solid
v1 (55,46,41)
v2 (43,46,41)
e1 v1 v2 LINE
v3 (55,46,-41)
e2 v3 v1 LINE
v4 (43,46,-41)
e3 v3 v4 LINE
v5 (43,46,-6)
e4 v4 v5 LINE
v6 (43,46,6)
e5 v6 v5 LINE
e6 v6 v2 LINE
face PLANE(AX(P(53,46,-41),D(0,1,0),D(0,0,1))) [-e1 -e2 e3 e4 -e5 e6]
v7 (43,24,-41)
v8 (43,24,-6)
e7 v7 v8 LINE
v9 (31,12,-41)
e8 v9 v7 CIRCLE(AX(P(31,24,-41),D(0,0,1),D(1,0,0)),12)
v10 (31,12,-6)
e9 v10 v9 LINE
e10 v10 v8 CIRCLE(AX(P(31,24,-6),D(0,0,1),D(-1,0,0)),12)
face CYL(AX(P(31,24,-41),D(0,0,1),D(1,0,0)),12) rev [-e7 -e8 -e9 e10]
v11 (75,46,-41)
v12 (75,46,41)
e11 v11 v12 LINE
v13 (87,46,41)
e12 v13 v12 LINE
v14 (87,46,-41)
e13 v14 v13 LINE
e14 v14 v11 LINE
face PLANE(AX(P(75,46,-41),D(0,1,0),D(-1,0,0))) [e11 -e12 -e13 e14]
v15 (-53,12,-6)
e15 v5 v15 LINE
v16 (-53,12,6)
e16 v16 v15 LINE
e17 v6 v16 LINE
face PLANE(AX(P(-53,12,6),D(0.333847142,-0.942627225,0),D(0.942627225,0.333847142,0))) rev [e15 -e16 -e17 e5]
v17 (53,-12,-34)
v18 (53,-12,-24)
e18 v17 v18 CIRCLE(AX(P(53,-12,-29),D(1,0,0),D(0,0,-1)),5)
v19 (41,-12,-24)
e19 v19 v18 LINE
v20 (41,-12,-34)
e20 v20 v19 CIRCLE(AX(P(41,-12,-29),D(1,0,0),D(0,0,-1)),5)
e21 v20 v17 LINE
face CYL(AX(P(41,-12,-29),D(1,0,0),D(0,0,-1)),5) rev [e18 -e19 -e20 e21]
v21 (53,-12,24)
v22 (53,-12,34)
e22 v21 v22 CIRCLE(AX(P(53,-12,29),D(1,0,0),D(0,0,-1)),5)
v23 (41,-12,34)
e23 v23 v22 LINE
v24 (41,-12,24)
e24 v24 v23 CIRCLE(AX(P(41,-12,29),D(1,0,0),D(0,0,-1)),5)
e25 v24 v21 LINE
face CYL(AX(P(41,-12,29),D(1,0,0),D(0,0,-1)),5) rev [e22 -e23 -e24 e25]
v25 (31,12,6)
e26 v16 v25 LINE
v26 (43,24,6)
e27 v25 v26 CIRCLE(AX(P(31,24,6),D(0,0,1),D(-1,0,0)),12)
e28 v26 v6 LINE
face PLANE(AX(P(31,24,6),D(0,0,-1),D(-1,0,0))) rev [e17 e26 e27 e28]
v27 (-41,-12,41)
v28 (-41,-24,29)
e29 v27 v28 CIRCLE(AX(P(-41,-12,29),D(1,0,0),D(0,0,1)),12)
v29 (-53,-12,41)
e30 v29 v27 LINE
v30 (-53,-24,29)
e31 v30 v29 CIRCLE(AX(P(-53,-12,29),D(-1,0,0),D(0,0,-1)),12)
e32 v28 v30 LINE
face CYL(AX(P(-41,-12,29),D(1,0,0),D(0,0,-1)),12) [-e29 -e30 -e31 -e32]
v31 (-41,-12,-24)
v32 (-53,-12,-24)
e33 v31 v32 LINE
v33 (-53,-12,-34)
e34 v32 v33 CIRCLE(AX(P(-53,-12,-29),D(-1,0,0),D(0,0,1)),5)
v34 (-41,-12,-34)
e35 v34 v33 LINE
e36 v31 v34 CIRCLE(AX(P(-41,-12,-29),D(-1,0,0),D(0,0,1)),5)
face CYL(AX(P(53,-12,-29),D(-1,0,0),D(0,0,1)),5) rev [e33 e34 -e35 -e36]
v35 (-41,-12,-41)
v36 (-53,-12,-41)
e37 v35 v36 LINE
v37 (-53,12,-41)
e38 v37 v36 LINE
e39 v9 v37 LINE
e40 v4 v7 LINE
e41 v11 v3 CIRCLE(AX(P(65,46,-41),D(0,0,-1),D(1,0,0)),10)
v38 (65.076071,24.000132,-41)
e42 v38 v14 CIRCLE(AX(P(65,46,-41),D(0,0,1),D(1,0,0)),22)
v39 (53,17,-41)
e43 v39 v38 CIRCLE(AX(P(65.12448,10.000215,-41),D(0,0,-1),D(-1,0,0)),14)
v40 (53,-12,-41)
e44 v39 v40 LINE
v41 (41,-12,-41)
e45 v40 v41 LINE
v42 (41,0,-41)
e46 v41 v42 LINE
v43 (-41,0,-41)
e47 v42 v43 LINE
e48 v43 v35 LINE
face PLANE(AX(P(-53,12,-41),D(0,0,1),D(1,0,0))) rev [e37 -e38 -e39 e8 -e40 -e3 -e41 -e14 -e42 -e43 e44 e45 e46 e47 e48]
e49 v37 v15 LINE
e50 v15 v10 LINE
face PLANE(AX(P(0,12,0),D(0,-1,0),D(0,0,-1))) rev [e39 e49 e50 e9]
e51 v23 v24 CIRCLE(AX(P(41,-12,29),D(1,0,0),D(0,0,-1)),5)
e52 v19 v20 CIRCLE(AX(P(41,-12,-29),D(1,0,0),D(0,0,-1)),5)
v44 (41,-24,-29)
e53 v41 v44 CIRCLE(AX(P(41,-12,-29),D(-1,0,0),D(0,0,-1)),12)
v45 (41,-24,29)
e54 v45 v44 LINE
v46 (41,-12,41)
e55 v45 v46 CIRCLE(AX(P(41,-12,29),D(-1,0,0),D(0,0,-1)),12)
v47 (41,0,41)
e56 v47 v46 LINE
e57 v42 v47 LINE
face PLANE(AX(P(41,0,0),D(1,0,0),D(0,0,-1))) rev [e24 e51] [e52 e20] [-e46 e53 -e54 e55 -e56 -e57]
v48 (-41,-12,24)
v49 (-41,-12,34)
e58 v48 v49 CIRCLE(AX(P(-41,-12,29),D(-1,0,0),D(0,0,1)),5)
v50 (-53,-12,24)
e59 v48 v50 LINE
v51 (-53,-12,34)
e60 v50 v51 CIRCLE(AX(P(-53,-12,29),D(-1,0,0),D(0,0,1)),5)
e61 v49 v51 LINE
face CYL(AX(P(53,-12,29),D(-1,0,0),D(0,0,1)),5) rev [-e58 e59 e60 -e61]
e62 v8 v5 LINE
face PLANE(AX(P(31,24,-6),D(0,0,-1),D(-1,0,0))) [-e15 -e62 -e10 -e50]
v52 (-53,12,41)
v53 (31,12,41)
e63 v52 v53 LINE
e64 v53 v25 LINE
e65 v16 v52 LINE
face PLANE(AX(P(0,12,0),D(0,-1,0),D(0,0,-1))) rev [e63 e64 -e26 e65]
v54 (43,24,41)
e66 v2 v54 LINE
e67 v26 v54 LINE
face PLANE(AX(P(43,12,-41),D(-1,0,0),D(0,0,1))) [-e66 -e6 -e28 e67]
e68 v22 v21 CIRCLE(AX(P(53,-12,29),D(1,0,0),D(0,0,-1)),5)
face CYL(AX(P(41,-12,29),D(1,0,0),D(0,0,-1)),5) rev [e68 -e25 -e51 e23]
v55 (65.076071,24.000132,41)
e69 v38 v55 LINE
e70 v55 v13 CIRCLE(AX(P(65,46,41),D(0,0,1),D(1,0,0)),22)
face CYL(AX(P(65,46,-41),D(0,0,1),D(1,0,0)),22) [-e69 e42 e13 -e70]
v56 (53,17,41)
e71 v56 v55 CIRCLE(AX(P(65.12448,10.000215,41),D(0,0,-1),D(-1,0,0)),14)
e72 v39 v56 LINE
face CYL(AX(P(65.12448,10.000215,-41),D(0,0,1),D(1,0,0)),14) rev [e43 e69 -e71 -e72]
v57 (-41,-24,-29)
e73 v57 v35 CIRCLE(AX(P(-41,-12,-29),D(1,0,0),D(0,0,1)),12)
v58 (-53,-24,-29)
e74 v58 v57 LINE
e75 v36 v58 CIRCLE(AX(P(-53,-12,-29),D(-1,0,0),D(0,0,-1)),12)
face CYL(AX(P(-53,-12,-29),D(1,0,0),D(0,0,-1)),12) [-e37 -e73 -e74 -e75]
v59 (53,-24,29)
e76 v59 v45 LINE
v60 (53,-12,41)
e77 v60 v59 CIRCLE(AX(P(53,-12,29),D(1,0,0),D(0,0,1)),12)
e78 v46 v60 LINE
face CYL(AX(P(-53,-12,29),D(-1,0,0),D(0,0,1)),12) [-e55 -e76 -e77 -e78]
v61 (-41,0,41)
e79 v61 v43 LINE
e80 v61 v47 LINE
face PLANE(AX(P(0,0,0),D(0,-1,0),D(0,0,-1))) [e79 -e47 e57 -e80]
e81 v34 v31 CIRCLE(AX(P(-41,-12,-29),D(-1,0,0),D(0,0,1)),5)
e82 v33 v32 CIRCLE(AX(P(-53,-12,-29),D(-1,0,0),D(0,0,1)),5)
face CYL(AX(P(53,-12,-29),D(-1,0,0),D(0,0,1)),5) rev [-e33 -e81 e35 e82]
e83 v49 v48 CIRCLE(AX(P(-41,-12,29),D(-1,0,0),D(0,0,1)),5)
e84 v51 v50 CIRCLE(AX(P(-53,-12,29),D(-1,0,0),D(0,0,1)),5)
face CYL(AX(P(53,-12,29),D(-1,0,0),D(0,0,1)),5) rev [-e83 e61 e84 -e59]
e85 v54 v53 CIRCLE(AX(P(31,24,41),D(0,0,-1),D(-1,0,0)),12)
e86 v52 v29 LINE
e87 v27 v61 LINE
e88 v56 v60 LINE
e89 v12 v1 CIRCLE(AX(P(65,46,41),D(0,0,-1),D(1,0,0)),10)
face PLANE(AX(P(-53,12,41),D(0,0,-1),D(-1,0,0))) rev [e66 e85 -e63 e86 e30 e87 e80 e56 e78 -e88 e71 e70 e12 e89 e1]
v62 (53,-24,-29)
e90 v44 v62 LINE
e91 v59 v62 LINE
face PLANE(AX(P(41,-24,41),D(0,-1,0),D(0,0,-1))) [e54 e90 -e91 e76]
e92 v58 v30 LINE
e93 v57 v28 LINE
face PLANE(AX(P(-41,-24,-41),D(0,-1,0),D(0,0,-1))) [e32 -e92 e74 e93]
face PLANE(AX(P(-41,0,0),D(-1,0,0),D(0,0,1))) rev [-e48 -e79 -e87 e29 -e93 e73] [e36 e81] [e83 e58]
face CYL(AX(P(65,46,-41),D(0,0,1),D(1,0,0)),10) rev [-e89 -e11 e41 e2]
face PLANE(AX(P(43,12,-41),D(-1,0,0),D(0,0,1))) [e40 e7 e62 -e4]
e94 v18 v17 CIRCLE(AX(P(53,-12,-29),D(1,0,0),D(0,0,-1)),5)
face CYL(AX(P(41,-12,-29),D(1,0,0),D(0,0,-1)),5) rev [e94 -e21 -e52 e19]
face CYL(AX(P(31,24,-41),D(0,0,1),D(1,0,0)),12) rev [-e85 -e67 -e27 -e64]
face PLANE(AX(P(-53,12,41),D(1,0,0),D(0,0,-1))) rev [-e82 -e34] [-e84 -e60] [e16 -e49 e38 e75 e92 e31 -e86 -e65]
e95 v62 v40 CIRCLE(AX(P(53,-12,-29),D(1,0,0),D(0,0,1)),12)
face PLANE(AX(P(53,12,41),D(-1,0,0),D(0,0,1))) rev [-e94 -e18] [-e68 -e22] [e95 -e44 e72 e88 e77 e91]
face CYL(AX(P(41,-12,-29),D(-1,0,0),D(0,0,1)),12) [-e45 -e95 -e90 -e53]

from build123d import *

# Parameters (mm, degrees)
BASE_PLATE_SKETCH_W       = 106
BASE_PLATE_SKETCH_H       = 82
BASE_PLATE_DEPTH          = 12
UPRIGHT_WALL_SKETCH_W     = 10
UPRIGHT_WALL_SKETCH_H     = 34
UPRIGHT_WALL_DEPTH        = 82
WALL_ROOT_FILLET_R12_R    = 12
MOUNTING_LUG_1_SKETCH_W   = 82
MOUNTING_LUG_1_SKETCH_H   = 24
MOUNTING_LUG_1_DEPTH      = 12
LUG_1_CORNER_FILLET_R12_R = 12
LUG_1_HOLE_SKETCH_R       = 5
LUG_1_MOUNTING_HOLE_DEPTH = 123.609135059
MOUNTING_LUG_2_SKETCH_W   = 82
MOUNTING_LUG_2_SKETCH_H   = 24
MOUNTING_LUG_2_DEPTH      = 12
LUG_2_CORNER_FILLET_R12_R = 12
LUG_START                 = -12
LUG_2_HOLE_SKETCH_R       = 5
LUG_2_MOUNTING_HOLE_DEPTH = 12
SIDE_SUPPORT_DEPTH        = 6
GROOVED_CLAMP_RAIL_DEPTH  = 82


with BuildPart() as part:
    # Base Plate Sketch → Base Plate (new body)
    with BuildSketch(Plane(origin=(0, 0, 0), x_dir=(1, 0, 0), z_dir=(0, 1, 0))):
        Rectangle(BASE_PLATE_SKETCH_W, BASE_PLATE_SKETCH_H)
    extrude(amount=BASE_PLATE_DEPTH)

    # Upright Wall Sketch → Upright Wall (add)
    with BuildSketch(Plane.XY.offset(41)):
        with Locations((48, 29)):
            Rectangle(UPRIGHT_WALL_SKETCH_W, UPRIGHT_WALL_SKETCH_H)
    extrude(amount=-UPRIGHT_WALL_DEPTH)

    # Wall Root Fillet R12
    wall_root_fillet_r12_edges = [part.edges().sort_by_distance(p)[0] for p in [
        (43, 12, 0),
    ]]
    fillet(wall_root_fillet_r12_edges, radius=WALL_ROOT_FILLET_R12_R)

    # Mounting Lug 1 Sketch → Mounting Lug 1 (add)
    with BuildSketch(Plane.ZY.offset(53)):
        with Locations((0, -12)):
            Rectangle(MOUNTING_LUG_1_SKETCH_W, MOUNTING_LUG_1_SKETCH_H)
    extrude(amount=-MOUNTING_LUG_1_DEPTH)

    # Lug 1 Corner Fillet R12
    lug_1_corner_fillet_r12_edges = [part.edges().sort_by_distance(p)[0] for p in [
        (-47, -24, -41),
        (-47, -24, 41),
    ]]
    fillet(lug_1_corner_fillet_r12_edges, radius=LUG_1_CORNER_FILLET_R12_R)

    # Lug 1 Hole Sketch → Lug 1 Mounting Hole (cut, through all)
    with BuildSketch(Plane.ZY.offset(53)):
        with Locations((-29, -12)):
            Circle(LUG_1_HOLE_SKETCH_R)
        with Locations((29, -12)):
            Circle(LUG_1_HOLE_SKETCH_R)
    extrude(amount=-LUG_1_MOUNTING_HOLE_DEPTH, mode=Mode.SUBTRACT)

    # Mounting Lug 2 Sketch → Mounting Lug 2 (add)
    with BuildSketch(Plane(origin=(53, 0, 0), x_dir=(0, 0, -1), z_dir=(1, 0, 0))):
        with Locations((0, -12)):
            Rectangle(MOUNTING_LUG_2_SKETCH_W, MOUNTING_LUG_2_SKETCH_H)
    extrude(amount=-MOUNTING_LUG_2_DEPTH)

    # Lug 2 Corner Fillet R12
    lug_2_corner_fillet_r12_edges = [part.edges().sort_by_distance(p)[0] for p in [
        (47, -24, 41),
        (47, -24, -41),
    ]]
    fillet(lug_2_corner_fillet_r12_edges, radius=LUG_2_CORNER_FILLET_R12_R)

    # Lug 2 Hole Sketch → Lug 2 Mounting Hole (cut)
    with BuildSketch(Plane(origin=(53, 0, 0), x_dir=(0, 0, -1), z_dir=(1, 0, 0)).offset(LUG_START)):
        with Locations(Location((-29, -12, 0), (0, 0, 180))):
            Circle(LUG_2_HOLE_SKETCH_R)
        with Locations(Location((29, -12, 0), (0, 0, 180))):
            Circle(LUG_2_HOLE_SKETCH_R)
    extrude(amount=LUG_2_MOUNTING_HOLE_DEPTH, mode=Mode.SUBTRACT)

    # Side Support Sketch → Side Support (add, symmetric)
    with BuildSketch(Plane.XY):
        with BuildLine():
            Line((-53, 12), (43, 46))
            Line((43, 46), (43, 24))
            ThreePointArc((43, 24), (39.485281374, 15.514718626), (31, 12))
            Line((31, 12), (-53, 12))
        make_face()
    extrude(amount=SIDE_SUPPORT_DEPTH, both=True)

    # Clamp Rail Profile Sketch → Grooved Clamp Rail (add)
    with BuildSketch(Plane.XY.offset(41)):
        with BuildLine():
            Line((53, 46), (55, 46))
            ThreePointArc((55, 46), (65, 36), (75, 46))
            Line((75, 46), (87, 46))
            ThreePointArc((87, 46), (80.583221155, 30.470569282), (65.076071052, 24.000131519))
            ThreePointArc((65.076071052, 24.000131519), (58.103421188, 22.112388202), (53, 17))
            Line((53, 17), (53, 46))
        make_face()
    extrude(amount=-GROOVED_CLAMP_RAIL_DEPTH)


solid = part.part
